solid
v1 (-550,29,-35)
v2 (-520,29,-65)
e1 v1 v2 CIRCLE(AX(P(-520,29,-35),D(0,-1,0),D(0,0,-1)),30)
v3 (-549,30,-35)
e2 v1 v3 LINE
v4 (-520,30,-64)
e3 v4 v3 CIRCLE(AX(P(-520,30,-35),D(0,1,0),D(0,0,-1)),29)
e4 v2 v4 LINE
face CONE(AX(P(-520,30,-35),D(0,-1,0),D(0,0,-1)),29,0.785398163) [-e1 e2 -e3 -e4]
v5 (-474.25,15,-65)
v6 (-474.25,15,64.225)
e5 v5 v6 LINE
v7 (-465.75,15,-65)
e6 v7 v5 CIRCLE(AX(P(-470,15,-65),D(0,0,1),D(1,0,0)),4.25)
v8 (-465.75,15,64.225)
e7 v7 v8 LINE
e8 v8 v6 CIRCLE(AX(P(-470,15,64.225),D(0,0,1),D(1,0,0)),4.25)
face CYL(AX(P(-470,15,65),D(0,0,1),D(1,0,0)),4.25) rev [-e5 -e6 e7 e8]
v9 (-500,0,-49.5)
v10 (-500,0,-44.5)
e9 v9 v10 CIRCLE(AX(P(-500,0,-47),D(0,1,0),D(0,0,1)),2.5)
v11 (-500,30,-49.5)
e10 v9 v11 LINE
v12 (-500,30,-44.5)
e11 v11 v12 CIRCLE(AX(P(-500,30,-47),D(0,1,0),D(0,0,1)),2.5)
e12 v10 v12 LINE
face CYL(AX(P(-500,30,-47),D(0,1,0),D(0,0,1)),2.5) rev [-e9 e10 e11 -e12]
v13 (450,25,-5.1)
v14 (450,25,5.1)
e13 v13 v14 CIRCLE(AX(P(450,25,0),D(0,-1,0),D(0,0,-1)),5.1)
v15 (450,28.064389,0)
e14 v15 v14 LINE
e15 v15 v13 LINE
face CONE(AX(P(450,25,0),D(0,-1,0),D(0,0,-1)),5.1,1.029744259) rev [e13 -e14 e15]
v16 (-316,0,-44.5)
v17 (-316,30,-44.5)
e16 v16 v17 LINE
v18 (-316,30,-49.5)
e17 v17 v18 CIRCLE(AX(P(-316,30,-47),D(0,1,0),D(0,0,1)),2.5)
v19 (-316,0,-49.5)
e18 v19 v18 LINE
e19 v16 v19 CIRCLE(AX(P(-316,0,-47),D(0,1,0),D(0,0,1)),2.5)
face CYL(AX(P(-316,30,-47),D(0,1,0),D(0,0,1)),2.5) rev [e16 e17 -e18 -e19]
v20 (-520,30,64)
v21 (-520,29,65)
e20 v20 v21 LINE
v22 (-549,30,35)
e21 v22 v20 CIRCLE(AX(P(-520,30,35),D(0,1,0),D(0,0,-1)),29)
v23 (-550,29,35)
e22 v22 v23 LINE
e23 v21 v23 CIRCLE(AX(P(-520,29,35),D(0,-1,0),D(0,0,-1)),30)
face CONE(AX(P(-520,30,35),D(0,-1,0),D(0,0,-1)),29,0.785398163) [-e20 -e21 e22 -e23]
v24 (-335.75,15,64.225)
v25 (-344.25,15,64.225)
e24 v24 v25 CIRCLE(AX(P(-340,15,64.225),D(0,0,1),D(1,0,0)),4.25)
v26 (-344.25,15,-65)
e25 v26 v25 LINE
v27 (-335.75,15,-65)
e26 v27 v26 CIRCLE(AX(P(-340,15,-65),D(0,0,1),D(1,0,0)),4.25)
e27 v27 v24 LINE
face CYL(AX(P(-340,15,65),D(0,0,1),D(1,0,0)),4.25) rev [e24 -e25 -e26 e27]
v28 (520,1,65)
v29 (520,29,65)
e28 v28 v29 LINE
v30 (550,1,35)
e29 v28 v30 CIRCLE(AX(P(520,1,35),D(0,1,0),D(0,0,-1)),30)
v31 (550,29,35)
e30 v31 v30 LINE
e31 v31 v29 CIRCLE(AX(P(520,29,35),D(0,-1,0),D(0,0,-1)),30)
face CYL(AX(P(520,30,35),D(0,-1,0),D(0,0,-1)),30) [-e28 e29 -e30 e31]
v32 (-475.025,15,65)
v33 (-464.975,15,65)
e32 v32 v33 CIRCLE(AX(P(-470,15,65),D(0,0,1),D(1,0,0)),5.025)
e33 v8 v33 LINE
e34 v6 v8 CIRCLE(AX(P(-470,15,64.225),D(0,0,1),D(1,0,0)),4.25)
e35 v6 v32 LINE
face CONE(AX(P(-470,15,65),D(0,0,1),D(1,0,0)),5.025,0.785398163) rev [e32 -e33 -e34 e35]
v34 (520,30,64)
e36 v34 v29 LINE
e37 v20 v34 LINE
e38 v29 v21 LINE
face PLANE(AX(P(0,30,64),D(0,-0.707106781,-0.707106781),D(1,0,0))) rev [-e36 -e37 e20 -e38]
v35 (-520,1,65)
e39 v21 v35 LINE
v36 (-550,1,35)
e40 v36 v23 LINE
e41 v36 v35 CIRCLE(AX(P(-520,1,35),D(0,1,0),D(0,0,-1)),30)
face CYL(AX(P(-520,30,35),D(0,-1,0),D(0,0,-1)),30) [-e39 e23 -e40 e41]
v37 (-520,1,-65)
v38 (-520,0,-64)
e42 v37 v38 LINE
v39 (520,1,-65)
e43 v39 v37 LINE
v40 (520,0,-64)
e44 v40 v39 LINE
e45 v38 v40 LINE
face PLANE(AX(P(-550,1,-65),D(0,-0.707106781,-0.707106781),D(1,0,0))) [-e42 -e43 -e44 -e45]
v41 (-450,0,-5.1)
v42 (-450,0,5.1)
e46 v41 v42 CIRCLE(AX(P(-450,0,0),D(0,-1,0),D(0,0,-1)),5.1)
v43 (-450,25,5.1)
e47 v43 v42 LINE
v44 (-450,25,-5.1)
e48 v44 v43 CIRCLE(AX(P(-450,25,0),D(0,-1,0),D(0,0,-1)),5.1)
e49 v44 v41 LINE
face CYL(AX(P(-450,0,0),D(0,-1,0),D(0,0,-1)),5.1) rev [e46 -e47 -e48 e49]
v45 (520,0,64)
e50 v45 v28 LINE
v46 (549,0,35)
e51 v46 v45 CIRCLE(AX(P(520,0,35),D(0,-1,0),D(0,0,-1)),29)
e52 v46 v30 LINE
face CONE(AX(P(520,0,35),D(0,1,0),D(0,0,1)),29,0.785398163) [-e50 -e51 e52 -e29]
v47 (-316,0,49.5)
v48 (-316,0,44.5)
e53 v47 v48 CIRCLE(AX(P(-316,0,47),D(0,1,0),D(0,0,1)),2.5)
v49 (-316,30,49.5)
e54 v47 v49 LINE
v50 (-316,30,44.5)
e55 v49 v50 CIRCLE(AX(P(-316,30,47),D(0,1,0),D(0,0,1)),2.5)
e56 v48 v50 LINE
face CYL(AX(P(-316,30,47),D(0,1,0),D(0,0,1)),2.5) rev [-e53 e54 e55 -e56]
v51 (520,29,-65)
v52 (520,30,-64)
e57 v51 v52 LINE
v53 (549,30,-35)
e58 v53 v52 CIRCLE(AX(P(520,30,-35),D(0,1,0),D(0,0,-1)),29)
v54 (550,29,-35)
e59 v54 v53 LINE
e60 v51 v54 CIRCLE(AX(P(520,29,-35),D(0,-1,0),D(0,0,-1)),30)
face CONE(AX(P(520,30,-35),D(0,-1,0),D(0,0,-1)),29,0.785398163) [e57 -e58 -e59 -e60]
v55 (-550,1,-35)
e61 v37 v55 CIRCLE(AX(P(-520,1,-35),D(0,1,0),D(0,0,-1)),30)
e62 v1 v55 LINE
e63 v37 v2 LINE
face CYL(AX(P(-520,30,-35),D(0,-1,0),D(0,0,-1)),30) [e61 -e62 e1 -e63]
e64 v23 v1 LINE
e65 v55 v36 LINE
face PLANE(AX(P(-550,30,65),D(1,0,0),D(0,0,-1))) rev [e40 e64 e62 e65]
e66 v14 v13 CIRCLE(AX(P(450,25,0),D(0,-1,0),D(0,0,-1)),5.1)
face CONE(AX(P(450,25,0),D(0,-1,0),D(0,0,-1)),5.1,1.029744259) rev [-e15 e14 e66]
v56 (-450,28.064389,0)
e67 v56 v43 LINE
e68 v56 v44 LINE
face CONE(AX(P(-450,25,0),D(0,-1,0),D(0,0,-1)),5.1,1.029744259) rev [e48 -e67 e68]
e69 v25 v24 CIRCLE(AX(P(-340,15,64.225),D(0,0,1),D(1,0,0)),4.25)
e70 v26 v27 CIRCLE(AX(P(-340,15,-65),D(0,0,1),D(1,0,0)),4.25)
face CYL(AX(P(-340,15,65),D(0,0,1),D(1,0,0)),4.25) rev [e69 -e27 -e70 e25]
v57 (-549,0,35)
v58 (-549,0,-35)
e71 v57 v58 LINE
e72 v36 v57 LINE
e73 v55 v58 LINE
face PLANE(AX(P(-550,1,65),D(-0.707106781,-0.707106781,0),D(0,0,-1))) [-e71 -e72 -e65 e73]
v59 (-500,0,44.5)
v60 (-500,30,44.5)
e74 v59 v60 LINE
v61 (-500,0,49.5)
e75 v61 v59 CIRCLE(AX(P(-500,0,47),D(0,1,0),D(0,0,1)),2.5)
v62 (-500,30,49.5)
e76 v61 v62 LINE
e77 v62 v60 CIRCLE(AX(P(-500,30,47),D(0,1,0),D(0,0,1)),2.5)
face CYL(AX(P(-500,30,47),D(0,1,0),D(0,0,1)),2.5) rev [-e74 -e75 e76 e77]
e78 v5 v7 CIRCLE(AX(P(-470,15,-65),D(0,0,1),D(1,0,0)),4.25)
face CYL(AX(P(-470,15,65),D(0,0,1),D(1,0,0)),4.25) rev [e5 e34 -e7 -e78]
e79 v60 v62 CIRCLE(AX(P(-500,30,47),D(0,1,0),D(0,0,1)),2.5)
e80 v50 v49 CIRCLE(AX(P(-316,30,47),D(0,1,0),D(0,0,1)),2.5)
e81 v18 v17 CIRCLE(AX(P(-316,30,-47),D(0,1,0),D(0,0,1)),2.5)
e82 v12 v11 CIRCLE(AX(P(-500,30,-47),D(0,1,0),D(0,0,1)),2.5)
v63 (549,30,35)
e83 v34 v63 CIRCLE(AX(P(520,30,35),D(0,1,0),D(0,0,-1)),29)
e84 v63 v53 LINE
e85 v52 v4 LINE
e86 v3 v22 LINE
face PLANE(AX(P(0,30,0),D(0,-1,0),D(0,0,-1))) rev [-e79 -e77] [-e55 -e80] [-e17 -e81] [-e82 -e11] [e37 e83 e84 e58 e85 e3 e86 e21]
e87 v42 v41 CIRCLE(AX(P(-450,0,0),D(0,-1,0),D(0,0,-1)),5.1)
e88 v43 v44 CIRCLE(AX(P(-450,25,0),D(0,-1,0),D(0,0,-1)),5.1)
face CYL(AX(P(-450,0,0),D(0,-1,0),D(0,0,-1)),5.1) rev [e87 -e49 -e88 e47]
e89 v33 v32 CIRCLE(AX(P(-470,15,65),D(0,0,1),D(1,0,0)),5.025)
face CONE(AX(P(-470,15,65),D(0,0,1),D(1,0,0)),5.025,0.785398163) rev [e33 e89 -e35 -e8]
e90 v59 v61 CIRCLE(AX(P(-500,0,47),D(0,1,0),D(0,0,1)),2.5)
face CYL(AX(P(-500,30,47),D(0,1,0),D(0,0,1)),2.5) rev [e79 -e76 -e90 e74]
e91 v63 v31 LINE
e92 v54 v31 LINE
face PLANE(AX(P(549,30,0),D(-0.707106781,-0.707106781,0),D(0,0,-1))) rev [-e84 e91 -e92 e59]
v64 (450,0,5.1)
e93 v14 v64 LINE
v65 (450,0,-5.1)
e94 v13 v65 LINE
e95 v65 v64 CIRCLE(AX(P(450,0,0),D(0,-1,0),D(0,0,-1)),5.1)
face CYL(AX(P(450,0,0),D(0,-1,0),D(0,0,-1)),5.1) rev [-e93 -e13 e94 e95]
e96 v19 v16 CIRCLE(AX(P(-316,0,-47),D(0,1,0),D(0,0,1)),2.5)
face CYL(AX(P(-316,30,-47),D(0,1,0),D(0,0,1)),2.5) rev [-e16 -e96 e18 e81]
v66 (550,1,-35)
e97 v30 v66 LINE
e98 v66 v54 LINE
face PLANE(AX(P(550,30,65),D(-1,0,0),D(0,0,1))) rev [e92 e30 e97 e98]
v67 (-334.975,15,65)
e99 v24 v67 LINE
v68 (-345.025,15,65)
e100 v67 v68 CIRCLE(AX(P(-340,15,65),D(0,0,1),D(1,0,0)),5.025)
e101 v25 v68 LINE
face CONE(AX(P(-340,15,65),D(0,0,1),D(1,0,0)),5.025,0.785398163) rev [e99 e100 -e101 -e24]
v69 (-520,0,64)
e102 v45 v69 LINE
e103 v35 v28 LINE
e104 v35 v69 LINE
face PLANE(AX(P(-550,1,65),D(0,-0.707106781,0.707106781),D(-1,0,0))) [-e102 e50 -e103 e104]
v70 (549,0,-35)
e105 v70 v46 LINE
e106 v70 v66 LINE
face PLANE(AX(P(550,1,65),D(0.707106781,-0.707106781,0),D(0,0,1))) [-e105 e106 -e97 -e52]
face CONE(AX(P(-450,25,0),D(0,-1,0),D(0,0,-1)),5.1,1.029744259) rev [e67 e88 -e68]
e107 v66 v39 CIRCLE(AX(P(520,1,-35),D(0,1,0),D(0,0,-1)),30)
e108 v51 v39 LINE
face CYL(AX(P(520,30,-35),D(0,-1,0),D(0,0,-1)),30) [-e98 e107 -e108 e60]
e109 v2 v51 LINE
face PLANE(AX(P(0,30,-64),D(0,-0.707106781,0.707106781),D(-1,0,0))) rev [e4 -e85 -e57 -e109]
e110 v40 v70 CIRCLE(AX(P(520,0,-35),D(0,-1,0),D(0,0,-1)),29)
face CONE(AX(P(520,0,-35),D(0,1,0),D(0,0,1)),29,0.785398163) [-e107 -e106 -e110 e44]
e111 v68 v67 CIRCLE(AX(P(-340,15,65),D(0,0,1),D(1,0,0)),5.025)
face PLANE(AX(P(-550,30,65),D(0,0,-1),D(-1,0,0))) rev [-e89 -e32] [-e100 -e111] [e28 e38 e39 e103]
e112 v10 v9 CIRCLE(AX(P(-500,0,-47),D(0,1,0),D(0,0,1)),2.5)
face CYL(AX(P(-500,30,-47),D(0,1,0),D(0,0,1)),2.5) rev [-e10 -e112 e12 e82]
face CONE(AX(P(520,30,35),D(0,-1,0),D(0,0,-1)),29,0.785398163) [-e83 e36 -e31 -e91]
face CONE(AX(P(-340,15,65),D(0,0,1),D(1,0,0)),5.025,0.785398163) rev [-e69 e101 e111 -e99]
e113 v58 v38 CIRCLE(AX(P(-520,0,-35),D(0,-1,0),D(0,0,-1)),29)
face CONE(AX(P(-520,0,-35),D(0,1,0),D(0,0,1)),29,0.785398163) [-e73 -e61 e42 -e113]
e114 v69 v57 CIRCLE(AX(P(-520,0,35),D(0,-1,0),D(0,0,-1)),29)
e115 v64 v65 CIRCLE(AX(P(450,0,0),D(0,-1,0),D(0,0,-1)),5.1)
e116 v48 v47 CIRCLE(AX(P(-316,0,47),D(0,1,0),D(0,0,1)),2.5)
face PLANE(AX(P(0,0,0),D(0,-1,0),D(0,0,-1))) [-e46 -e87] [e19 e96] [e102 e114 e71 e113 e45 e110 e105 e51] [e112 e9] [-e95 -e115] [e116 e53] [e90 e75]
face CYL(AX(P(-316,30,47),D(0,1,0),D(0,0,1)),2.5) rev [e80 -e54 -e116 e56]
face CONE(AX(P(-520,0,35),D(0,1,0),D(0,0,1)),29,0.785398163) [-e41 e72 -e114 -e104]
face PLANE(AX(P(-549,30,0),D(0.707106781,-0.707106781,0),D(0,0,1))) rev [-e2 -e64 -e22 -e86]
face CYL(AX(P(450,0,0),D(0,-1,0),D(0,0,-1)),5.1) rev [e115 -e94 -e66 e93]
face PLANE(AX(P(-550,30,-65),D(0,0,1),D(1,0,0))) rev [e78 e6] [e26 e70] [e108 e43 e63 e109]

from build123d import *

# Parameters (mm, degrees)
SKETCH1_W                    = 1100
SKETCH1_H                    = 130
BOSS_EXTRUDE1_DEPTH          = 30
M6_TAPPED_HOLE1_D            = 5
M12_TAPPED_HOLE1_D           = 10.2
M12_TAPPED_HOLE1_DEPTH       = 25
M12_TAPPED_HOLE1_TIP         = 3.064389157
FILLET1_R                    = 30
CHAMFER1_SIZE                = 1
M10_TAPPED_HOLE1_D           = 8.5
M10_TAPPED_HOLE1_CSINK_D     = 10.05
M10_TAPPED_HOLE1_CSINK_ANGLE = 90


with BuildPart() as part:
    # Sketch1 → Boss-Extrude1 (new body)
    with BuildSketch(Plane(origin=(0, 0, 0), x_dir=(1, 0, 0), z_dir=(0, 1, 0))):
        Rectangle(SKETCH1_W, SKETCH1_H)
    extrude(amount=BOSS_EXTRUDE1_DEPTH)

    # M6 Tapped Hole1 (through all)
    with Locations(Plane(origin=(0, 30, 0), x_dir=(1, 0, 0), z_dir=(0, 1, 0))):
        with Locations((-316, 47), (-316, -47), (-500, 47), (-500, -47)):
            Hole(M6_TAPPED_HOLE1_D / 2)

    # M12 Tapped Hole1
    with Locations(Plane(origin=(0, 0, 0), x_dir=(-1, 0, 0), z_dir=(0, -1, 0))):
        with Locations((450, 0), (-450, 0)):
            Hole(M12_TAPPED_HOLE1_D / 2, depth=M12_TAPPED_HOLE1_DEPTH)
            with Locations((0, 0, -(M12_TAPPED_HOLE1_DEPTH + M12_TAPPED_HOLE1_TIP / 2))):  # 118° drill point
                Cone(0, M12_TAPPED_HOLE1_D / 2, M12_TAPPED_HOLE1_TIP, mode=Mode.SUBTRACT)

    # Fillet1
    fillet1_edges = [part.edges().sort_by_distance(p)[0] for p in [
        (550, 15, 65),
        (-550, 15, 65),
        (-550, 15, -65),
        (550, 15, -65),
    ]]
    fillet(fillet1_edges, radius=FILLET1_R)

    # Chamfer1
    chamfer1_edges = [part.edges().sort_by_distance(p)[0] for p in [
        (-550, 0, 0),
        (-550, 30, 0),
        (550, 0, 0),
        (0, 0, 65),
        (0, 0, -65),
        (-541.213203436, 0, 56.213203436),
        (541.213203436, 0, 56.213203436),
        (541.213203436, 0, -56.213203436),
        (-541.213203436, 0, -56.213203436),
        (0, 30, -65),
        (550, 30, 0),
        (0, 30, 65),
        (-541.213203436, 30, 56.213203436),
        (541.213203436, 30, 56.213203436),
        (541.213203436, 30, -56.213203436),
        (-541.213203436, 30, -56.213203436),
    ]]
    chamfer(chamfer1_edges, length=CHAMFER1_SIZE)

    # M10 Tapped Hole1 (through all)
    with Locations(Plane.XY.offset(65)):
        with Locations((-470, 15), (-340, 15)):
            CounterSinkHole(M10_TAPPED_HOLE1_D / 2, M10_TAPPED_HOLE1_CSINK_D / 2, counter_sink_angle=M10_TAPPED_HOLE1_CSINK_ANGLE)


solid = part.part
